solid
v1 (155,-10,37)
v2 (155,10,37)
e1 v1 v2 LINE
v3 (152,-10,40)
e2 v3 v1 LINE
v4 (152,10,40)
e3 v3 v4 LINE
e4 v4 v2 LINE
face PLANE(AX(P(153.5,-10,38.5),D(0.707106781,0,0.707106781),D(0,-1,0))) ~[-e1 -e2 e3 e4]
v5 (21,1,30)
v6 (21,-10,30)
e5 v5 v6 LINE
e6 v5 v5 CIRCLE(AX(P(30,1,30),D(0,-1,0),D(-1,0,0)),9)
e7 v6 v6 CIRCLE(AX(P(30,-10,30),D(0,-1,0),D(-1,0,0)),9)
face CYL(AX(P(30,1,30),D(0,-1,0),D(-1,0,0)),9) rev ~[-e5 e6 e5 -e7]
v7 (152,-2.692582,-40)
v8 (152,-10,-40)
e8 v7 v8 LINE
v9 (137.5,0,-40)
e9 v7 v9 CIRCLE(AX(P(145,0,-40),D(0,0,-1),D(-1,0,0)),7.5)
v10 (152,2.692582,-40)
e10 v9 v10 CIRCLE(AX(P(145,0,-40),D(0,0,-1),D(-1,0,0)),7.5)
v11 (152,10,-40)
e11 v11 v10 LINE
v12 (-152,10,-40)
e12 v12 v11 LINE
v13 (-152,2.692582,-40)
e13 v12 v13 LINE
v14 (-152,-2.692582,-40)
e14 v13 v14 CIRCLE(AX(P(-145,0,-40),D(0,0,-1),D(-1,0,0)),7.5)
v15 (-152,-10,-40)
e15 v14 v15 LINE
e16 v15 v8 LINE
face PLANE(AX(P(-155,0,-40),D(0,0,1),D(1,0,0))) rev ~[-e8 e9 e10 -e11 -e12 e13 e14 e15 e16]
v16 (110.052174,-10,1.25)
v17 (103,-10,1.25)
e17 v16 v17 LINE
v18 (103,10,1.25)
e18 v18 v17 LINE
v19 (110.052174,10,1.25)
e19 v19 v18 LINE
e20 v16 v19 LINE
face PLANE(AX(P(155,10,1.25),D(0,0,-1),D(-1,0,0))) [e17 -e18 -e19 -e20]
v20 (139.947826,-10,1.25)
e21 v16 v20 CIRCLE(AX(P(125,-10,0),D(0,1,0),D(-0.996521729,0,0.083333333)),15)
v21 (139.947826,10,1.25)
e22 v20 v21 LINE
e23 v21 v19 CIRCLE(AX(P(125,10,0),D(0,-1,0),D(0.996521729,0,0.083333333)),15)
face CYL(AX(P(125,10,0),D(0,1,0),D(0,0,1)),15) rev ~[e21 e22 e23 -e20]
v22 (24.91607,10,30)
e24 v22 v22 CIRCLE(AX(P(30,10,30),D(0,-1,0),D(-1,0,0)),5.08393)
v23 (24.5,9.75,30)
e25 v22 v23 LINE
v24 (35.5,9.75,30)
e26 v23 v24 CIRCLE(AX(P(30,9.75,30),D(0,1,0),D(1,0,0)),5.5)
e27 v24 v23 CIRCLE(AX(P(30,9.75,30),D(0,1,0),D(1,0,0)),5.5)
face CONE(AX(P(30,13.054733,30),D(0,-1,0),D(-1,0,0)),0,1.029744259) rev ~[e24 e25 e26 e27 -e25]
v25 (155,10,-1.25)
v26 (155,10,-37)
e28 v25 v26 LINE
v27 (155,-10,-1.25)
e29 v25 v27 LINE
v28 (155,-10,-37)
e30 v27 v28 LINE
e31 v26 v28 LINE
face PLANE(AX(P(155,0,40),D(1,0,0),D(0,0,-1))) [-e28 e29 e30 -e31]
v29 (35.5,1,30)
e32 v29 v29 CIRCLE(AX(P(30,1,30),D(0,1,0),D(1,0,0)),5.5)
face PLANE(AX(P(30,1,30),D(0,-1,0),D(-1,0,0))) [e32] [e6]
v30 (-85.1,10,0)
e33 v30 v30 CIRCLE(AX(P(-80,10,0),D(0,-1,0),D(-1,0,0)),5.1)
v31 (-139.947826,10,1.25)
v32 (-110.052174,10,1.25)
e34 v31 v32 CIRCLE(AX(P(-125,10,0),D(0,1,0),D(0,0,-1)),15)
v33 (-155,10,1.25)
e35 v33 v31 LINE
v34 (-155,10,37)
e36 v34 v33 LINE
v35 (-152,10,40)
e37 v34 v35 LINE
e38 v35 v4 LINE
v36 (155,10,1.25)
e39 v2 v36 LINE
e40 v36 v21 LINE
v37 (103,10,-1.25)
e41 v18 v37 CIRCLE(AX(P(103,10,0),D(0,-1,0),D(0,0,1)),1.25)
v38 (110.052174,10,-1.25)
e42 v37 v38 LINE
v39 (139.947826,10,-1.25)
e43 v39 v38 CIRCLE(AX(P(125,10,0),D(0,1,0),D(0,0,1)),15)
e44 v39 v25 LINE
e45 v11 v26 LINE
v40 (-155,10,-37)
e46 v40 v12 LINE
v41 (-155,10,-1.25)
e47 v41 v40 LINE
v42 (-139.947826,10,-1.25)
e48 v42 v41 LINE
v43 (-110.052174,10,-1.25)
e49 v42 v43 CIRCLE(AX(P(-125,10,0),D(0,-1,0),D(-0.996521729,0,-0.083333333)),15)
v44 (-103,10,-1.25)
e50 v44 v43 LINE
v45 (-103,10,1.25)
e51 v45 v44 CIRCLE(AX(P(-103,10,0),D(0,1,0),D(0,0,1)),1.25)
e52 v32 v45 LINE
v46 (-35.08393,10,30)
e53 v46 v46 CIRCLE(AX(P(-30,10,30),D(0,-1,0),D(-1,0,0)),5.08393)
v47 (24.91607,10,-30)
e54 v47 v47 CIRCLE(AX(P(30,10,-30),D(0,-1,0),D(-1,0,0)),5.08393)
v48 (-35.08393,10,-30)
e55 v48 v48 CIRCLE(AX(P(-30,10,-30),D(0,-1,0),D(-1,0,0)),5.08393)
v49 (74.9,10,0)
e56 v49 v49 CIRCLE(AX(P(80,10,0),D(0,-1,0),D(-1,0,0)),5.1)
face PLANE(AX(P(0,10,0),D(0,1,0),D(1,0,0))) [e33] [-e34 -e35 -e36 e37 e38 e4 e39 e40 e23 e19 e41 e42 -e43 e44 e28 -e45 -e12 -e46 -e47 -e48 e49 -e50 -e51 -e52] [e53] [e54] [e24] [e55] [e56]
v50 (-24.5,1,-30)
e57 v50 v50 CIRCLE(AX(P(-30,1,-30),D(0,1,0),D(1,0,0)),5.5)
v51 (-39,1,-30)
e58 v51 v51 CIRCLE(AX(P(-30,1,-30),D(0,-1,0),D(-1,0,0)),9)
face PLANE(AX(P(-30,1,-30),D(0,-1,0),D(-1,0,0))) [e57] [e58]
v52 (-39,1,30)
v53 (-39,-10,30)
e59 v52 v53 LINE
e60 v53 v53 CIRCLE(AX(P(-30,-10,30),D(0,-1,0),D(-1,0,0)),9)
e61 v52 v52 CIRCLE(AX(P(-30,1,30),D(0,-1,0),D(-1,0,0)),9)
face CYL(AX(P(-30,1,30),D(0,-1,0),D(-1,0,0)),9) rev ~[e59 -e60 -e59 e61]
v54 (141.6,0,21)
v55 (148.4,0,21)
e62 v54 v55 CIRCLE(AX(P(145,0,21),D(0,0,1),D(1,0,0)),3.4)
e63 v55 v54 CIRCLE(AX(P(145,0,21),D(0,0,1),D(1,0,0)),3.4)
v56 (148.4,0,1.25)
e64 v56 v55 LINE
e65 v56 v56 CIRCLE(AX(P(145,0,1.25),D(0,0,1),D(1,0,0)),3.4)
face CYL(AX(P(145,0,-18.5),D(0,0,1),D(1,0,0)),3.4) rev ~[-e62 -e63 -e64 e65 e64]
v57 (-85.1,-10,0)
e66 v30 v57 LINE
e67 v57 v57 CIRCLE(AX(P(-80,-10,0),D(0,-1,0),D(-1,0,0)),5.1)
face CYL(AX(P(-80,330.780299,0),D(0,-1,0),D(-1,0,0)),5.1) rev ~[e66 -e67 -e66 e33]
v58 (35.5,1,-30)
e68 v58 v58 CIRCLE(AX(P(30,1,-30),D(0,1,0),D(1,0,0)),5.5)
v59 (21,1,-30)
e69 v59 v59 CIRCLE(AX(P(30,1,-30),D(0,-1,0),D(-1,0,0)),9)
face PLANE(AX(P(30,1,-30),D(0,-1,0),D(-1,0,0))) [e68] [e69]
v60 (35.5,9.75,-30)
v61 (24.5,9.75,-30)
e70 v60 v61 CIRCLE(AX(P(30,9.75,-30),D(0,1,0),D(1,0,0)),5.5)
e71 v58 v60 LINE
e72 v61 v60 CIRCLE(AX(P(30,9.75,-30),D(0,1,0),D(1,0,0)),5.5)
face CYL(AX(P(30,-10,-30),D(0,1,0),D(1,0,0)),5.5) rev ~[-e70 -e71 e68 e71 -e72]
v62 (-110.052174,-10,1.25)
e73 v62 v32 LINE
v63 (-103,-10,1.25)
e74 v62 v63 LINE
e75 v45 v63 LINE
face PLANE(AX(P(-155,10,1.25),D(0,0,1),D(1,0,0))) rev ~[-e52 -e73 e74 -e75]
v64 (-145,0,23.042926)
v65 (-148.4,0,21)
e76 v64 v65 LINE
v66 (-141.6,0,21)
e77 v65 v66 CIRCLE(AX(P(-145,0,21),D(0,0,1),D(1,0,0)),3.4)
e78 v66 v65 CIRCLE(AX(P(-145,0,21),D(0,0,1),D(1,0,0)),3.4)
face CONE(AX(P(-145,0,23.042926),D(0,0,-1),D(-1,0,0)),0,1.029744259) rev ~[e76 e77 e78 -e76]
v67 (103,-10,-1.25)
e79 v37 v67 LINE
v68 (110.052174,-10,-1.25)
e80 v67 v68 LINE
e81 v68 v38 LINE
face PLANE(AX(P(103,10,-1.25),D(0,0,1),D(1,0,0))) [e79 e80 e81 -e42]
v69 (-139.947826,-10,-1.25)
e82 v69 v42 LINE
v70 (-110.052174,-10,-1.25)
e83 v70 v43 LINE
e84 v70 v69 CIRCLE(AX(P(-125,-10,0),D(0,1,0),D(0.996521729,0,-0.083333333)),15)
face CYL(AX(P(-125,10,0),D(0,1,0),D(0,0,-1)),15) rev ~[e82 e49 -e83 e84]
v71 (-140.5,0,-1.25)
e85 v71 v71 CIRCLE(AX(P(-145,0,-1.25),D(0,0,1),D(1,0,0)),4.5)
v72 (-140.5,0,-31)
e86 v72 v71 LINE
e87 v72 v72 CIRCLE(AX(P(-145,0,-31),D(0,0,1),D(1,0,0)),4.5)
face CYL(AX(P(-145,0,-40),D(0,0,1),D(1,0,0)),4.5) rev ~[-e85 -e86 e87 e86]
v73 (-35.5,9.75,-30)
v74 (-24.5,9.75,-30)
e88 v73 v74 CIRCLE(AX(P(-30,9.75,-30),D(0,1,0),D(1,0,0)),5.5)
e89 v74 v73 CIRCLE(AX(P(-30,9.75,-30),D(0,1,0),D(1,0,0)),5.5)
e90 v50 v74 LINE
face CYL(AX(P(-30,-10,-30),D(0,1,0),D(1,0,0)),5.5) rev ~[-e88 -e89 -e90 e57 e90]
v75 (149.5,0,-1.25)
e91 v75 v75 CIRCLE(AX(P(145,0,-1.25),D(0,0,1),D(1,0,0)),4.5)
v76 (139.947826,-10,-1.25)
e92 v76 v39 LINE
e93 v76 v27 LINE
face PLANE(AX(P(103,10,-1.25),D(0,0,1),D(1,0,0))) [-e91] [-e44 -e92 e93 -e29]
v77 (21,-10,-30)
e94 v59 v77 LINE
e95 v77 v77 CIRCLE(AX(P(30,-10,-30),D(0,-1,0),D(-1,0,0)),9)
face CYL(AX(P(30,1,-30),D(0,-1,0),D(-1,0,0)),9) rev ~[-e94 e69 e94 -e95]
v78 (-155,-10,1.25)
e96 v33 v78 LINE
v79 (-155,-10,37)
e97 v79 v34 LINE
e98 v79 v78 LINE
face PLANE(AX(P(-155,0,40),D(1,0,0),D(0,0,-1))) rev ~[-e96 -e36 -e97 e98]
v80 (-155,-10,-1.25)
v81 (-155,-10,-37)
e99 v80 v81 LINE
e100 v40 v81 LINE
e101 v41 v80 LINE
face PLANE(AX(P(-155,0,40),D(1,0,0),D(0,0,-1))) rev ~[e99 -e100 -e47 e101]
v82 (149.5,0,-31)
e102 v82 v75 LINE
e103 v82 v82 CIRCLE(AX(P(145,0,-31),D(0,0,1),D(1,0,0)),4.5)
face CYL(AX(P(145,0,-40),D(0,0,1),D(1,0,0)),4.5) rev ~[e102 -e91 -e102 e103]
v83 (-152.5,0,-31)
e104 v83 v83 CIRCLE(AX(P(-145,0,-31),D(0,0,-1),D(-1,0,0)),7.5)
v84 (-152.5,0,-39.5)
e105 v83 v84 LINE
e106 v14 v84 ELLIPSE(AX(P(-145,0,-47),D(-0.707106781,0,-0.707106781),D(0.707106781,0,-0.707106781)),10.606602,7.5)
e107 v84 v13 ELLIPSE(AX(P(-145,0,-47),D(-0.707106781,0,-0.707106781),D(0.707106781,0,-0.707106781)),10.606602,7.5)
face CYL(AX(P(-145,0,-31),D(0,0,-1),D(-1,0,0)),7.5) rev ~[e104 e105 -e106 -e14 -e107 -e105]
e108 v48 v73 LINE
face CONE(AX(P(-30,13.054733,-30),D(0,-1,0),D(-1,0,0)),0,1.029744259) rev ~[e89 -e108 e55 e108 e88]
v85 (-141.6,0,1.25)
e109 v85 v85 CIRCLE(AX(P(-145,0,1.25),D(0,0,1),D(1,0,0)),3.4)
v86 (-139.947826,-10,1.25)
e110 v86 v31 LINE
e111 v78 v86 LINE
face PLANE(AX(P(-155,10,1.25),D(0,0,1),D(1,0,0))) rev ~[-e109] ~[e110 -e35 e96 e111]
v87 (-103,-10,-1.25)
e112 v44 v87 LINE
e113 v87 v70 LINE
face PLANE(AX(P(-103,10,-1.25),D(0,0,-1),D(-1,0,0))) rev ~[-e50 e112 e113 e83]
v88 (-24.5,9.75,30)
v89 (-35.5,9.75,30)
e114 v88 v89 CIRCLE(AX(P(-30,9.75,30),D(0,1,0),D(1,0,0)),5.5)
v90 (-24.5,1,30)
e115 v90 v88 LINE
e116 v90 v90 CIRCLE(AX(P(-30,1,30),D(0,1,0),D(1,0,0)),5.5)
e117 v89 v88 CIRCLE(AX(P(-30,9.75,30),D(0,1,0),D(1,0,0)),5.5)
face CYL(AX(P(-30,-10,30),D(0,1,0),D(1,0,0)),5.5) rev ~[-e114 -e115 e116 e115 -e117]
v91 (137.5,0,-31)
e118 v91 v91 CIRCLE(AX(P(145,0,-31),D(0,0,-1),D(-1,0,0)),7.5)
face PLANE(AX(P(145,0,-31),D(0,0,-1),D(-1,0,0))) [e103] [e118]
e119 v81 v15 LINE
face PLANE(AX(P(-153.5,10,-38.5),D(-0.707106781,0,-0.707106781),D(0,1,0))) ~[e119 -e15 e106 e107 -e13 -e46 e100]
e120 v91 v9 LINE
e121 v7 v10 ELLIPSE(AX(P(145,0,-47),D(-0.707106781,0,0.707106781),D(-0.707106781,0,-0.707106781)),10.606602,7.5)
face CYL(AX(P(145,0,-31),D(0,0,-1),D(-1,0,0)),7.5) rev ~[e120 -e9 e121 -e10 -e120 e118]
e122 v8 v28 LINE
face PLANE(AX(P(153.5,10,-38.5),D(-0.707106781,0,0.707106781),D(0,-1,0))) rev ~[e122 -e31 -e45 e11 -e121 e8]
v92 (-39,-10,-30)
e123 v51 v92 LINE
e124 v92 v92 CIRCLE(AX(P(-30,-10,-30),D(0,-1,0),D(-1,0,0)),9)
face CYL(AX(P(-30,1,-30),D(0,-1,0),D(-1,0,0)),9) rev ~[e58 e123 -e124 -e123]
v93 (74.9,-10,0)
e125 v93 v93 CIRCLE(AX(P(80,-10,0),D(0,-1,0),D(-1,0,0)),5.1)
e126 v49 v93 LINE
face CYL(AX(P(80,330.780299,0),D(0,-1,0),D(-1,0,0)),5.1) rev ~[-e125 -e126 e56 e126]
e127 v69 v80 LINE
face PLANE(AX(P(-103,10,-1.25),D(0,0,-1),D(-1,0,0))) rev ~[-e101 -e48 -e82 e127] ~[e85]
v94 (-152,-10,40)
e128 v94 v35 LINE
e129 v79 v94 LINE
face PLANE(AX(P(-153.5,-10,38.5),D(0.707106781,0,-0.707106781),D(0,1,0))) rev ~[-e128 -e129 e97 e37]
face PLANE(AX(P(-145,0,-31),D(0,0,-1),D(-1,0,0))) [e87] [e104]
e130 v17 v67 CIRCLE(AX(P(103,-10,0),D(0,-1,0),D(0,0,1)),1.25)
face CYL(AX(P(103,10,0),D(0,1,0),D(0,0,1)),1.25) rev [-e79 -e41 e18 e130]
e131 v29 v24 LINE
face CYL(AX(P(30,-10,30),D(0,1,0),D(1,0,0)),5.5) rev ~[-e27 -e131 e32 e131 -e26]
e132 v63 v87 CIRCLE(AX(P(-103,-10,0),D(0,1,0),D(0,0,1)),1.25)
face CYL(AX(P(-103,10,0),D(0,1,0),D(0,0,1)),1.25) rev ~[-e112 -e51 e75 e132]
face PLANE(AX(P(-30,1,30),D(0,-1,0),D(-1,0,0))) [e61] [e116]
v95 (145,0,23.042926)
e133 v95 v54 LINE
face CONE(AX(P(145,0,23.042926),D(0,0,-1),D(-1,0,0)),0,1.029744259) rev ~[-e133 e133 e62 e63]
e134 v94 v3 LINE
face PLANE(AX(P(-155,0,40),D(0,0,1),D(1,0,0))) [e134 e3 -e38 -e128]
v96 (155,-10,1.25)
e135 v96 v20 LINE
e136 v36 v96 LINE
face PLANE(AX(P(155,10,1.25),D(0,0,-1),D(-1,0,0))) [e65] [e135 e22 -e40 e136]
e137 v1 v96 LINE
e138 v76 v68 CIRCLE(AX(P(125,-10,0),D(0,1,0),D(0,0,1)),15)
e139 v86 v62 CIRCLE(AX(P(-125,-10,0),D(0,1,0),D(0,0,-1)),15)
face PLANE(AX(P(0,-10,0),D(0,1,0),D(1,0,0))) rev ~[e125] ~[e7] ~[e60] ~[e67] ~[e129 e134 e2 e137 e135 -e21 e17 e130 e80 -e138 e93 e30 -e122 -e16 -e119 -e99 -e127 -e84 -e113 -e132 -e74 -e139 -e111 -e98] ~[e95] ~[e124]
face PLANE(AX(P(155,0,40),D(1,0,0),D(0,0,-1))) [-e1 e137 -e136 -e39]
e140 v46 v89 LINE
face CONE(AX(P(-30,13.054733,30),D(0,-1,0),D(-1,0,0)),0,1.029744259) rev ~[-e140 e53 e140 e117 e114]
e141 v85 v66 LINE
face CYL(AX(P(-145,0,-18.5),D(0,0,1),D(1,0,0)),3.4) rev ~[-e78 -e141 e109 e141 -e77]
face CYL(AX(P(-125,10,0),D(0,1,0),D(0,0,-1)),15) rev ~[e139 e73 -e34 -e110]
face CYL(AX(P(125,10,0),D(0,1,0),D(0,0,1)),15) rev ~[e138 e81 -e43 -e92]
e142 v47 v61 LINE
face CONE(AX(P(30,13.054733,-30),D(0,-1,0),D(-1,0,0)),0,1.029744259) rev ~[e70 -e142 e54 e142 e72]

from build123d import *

# Parameters (mm, degrees)
SKETCH_1_W                  = 310
SKETCH_1_H                  = 80
EXTRUDE_1_DEPTH             = 10
SKETCH_2_R                  = 15
CUT_EXTRUDE_1_DEPTH         = 20
CHAMFER_1_SIZE              = 3
CUT_EXTRUDE_2_DEPTH         = 20
HOLE_WIZARD_2_D             = 9
HOLE_WIZARD_2_DEPTH         = 40
HOLE_WIZARD_2_CBORE_D       = 15
HOLE_WIZARD_2_CBORE_DEPTH   = 9
HOLE_WIZARD_2_TIP           = 2.703872786
HOLE_WIZARD_M8_1_D          = 6.8
HOLE_WIZARD_M8_1_DEPTH      = 19.75
HOLE_WIZARD_M8_1_TIP        = 2.042926105
HOLE_WIZARD_2_2_D           = 11
HOLE_WIZARD_2_2_DEPTH       = 19.75
HOLE_WIZARD_2_2_CBORE_D     = 18
HOLE_WIZARD_2_2_CBORE_DEPTH = 11
HOLE_WIZARD_2_2_TIP         = 3.304733405
HOLE_WIZARD_M12_1_D         = 10.2


with BuildPart() as part:
    # 草图1 → 凸台-拉伸1 (new, symmetric)
    with BuildSketch(Plane(origin=(0, 0, 0), x_dir=(1, 0, 0), z_dir=(0, 1, 0))):
        Rectangle(SKETCH_1_W, SKETCH_1_H)
    extrude(amount=EXTRUDE_1_DEPTH, both=True)

    # 草图2 → 切除-拉伸1 (cut)
    with BuildSketch(Plane(origin=(0, 10, 0), x_dir=(1, 0, 0), z_dir=(0, 1, 0))):
        with Locations(Location((125, 0, 0), (0, 0, 270))):
            Circle(SKETCH_2_R)
        with Locations(Location((-125, 0, 0), (0, 0, 90))):
            Circle(SKETCH_2_R)
    extrude(amount=-CUT_EXTRUDE_1_DEPTH, mode=Mode.SUBTRACT)

    # 倒角1
    chamfer_1_edges = [part.edges().sort_by_distance(p)[0] for p in [
        (155, 0, 40),
        (-155, 0, 40),
        (-155, 0, -40),
        (155, 0, -40),
    ]]
    chamfer(chamfer_1_edges, length=CHAMFER_1_SIZE)

    # 草图3 → 切除-拉伸2 (cut)
    with BuildSketch(Plane(origin=(0, 10, 0), x_dir=(1, 0, 0), z_dir=(0, 1, 0))):
        with BuildLine():
            Line((155, -1.25), (103, -1.25))
            ThreePointArc((103, -1.25), (101.75, 0), (103, 1.25))
            Line((103, 1.25), (155, 1.25))
            ThreePointArc((155, 1.25), (156.25, 0), (155, -1.25))
        make_face()
        with BuildLine():
            Line((-155, -1.25), (-103, -1.25))
            ThreePointArc((-103, -1.25), (-101.75, 0), (-103, 1.25))
            Line((-103, 1.25), (-155, 1.25))
            ThreePointArc((-155, 1.25), (-156.25, 0), (-155, -1.25))
        make_face()
    extrude(amount=-CUT_EXTRUDE_2_DEPTH, mode=Mode.SUBTRACT)

    # Hole Wizard 2
    with Locations(Plane(origin=(0, 0, -40), x_dir=(-1, 0, 0), z_dir=(0, 0, -1))):
        with Locations((-145, 0), (145, 0)):
            CounterBoreHole(HOLE_WIZARD_2_D / 2, HOLE_WIZARD_2_CBORE_D / 2, HOLE_WIZARD_2_CBORE_DEPTH, depth=HOLE_WIZARD_2_DEPTH)
            with Locations((0, 0, -(HOLE_WIZARD_2_DEPTH + HOLE_WIZARD_2_TIP / 2))):  # 118° drill point
                Cone(0, HOLE_WIZARD_2_D / 2, HOLE_WIZARD_2_TIP, mode=Mode.SUBTRACT)

    # M8 螺纹孔1
    with Locations(Plane(origin=(0, 0, 1.25), x_dir=(-1, 0, 0), z_dir=(0, 0, -1))):
        with Locations((-145, 0), (145, 0)):
            Hole(HOLE_WIZARD_M8_1_D / 2, depth=HOLE_WIZARD_M8_1_DEPTH)
            with Locations((0, 0, -(HOLE_WIZARD_M8_1_DEPTH + HOLE_WIZARD_M8_1_TIP / 2))):  # 118° drill point
                Cone(0, HOLE_WIZARD_M8_1_D / 2, HOLE_WIZARD_M8_1_TIP, mode=Mode.SUBTRACT)

    # Hole Wizard 2 2
    with Locations(Plane(origin=(0, -10, 0), x_dir=(-1, 0, 0), z_dir=(0, -1, 0))):
        with Locations((-30, 30), (30, 30), (30, -30), (-30, -30)):
            CounterBoreHole(HOLE_WIZARD_2_2_D / 2, HOLE_WIZARD_2_2_CBORE_D / 2, HOLE_WIZARD_2_2_CBORE_DEPTH, depth=HOLE_WIZARD_2_2_DEPTH)
            with Locations((0, 0, -(HOLE_WIZARD_2_2_DEPTH + HOLE_WIZARD_2_2_TIP / 2))):  # 118° drill point
                Cone(0, HOLE_WIZARD_2_2_D / 2, HOLE_WIZARD_2_2_TIP, mode=Mode.SUBTRACT)

    # M12 螺纹孔1 (through all)
    with Locations(Plane(origin=(0, 10, 0), x_dir=(1, 0, 0), z_dir=(0, 1, 0))):
        with Locations((80, 0), (-80, 0)):
            Hole(HOLE_WIZARD_M12_1_D / 2)


solid = part.part
